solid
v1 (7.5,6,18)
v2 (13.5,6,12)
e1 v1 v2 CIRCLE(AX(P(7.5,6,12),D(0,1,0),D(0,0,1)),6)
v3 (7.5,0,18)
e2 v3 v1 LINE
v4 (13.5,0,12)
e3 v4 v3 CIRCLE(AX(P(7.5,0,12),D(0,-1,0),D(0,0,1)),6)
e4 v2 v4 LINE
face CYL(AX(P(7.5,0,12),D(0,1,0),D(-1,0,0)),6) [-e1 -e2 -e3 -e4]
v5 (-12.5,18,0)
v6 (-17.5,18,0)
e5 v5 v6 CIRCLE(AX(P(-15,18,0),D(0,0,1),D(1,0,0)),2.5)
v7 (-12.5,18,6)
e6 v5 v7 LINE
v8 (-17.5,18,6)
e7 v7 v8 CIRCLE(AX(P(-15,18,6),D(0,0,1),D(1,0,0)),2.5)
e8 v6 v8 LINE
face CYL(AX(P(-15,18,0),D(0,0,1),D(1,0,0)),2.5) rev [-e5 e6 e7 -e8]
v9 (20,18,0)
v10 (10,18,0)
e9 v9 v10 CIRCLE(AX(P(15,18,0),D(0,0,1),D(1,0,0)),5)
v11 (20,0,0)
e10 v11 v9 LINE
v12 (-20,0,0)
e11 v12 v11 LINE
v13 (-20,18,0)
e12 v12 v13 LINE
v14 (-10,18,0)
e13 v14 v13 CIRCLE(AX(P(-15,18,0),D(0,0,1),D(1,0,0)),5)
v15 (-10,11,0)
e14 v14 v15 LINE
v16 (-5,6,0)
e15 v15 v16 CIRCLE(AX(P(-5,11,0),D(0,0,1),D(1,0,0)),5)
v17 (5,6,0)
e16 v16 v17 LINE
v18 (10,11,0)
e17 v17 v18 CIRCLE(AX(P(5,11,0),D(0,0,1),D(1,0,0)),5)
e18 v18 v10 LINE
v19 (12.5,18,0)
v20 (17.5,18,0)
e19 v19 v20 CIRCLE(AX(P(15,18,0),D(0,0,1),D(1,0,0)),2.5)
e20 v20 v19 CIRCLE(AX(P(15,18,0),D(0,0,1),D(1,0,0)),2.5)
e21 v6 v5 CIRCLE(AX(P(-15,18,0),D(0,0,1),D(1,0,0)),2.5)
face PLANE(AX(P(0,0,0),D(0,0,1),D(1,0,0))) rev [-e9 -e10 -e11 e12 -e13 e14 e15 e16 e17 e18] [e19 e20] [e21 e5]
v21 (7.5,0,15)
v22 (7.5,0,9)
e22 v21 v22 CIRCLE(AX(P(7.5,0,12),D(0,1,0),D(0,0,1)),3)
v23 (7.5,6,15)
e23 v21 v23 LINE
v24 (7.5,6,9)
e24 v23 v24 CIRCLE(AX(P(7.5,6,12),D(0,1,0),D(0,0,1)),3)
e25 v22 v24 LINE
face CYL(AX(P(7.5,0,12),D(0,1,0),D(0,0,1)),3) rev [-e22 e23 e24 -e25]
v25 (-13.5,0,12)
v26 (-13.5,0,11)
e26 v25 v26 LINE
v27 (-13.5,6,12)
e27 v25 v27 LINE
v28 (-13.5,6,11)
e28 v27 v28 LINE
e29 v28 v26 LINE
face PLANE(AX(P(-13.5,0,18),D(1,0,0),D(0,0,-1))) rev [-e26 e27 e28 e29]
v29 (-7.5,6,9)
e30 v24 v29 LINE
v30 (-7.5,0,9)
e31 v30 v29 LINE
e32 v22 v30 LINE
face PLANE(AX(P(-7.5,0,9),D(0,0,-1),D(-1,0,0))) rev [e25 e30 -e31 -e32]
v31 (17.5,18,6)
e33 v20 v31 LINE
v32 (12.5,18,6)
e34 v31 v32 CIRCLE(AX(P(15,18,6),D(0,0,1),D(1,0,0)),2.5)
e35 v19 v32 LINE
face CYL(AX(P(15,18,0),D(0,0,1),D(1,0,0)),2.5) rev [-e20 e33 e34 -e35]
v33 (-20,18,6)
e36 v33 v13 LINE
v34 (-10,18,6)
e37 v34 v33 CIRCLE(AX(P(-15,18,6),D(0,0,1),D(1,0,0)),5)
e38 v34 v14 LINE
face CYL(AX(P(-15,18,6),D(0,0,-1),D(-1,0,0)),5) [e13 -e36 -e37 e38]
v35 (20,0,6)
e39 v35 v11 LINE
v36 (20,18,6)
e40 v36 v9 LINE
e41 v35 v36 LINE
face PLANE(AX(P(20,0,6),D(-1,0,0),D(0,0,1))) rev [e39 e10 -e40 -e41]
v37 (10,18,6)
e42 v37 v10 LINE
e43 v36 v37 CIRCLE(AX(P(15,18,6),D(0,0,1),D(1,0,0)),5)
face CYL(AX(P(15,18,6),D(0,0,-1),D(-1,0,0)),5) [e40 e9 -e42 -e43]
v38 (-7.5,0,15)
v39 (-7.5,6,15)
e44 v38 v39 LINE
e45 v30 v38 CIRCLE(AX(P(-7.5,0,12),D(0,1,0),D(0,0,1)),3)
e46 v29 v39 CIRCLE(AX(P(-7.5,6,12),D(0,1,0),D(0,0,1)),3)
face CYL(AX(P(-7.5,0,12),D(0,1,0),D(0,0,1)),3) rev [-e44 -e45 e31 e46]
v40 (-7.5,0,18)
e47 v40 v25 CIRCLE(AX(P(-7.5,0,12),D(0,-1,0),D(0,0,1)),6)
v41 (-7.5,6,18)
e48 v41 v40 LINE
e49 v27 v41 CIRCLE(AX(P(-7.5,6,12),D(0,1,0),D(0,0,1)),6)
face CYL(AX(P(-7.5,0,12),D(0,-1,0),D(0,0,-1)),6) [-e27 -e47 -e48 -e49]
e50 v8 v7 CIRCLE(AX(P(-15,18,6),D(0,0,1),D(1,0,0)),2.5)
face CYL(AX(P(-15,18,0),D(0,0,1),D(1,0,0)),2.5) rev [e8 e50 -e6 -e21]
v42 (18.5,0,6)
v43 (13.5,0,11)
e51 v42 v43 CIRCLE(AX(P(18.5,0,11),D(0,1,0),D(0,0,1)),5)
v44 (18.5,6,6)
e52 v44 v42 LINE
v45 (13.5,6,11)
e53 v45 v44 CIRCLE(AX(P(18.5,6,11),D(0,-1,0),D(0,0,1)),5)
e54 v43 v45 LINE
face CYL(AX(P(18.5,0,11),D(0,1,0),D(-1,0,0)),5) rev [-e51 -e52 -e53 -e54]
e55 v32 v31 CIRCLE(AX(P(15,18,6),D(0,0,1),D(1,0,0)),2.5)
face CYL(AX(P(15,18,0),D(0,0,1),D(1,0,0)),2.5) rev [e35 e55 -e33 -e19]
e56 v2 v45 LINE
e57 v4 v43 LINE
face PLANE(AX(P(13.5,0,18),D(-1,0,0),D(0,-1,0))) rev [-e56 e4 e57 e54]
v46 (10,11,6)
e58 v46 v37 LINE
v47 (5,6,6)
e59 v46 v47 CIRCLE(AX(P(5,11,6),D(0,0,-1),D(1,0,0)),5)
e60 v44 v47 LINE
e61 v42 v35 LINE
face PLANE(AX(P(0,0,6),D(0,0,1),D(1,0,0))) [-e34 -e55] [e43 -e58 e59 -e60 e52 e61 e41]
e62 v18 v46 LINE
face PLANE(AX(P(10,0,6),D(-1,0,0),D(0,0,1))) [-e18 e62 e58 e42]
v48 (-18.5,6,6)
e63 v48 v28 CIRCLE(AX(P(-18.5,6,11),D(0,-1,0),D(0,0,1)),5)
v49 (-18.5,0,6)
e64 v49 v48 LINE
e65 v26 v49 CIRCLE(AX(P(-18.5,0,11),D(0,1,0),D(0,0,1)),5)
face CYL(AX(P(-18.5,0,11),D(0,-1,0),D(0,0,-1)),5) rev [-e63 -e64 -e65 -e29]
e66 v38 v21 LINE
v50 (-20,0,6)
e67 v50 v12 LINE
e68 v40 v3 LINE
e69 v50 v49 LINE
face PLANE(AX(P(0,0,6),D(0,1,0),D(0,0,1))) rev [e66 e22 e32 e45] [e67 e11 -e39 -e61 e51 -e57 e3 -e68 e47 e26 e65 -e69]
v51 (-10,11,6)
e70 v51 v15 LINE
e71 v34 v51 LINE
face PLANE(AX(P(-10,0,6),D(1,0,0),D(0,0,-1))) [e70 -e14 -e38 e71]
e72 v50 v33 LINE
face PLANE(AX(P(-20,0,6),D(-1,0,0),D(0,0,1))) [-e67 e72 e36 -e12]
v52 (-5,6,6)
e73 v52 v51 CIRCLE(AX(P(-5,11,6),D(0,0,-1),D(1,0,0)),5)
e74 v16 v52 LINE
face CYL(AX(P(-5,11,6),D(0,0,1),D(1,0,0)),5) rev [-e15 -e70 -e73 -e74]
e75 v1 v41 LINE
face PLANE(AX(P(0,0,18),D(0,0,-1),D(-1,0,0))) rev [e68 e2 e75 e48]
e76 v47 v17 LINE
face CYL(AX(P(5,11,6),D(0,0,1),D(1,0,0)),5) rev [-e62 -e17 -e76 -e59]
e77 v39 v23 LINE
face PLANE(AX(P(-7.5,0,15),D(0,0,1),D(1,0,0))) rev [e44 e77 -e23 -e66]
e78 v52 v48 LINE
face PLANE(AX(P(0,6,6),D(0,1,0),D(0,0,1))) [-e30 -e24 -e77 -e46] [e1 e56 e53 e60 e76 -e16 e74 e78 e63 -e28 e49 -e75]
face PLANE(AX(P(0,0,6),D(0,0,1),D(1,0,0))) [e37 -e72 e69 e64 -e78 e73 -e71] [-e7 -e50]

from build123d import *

# Parameters (mm, degrees)
BRACKET_PROFILE_DEPTH     = 6
UPRIGHT_ROUNDS_R5_R       = 5
BASE_PLATE_SKETCH_W       = 27
BASE_PLATE_SKETCH_H       = 6
BASE_PLATE_DEPTH          = 12
BASE_PLATE_ROUNDS_R6_R    = 6
BASE_UPRIGHT_FILLETS_R5_R = 5
BASE_SLOT_DEPTH           = 6
PIVOT_HOLES_SKETCH_R      = 2.5
PIVOT_HOLES_2X_5_DEPTH    = 6


with BuildPart() as part:
    # Bracket Profile Sketch → Bracket Profile (new body)
    with BuildSketch(Plane.XY):
        with BuildLine():
            Line((-20, 0), (20, 0))
            Line((20, 0), (20, 18))
            ThreePointArc((20, 18), (15, 23), (10, 18))
            Line((10, 18), (10, 6))
            Line((10, 6), (-10, 6))
            Line((-10, 6), (-10, 18))
            ThreePointArc((-10, 18), (-15, 23), (-20, 18))
            Line((-20, 18), (-20, 0))
        make_face()
    extrude(amount=BRACKET_PROFILE_DEPTH)

    # Upright Rounds R5
    upright_rounds_r5_edges = [part.edges().sort_by_distance(p)[0] for p in [
        (-10, 6, 3),
        (10, 6, 3),
    ]]
    fillet(upright_rounds_r5_edges, radius=UPRIGHT_ROUNDS_R5_R)

    # Base Plate Sketch → Base Plate (add)
    with BuildSketch(Plane.XY.offset(6)):
        with Locations((0, 3)):
            Rectangle(BASE_PLATE_SKETCH_W, BASE_PLATE_SKETCH_H)
    extrude(amount=BASE_PLATE_DEPTH)

    # Base Plate Rounds R6
    base_plate_rounds_r6_edges = [part.edges().sort_by_distance(p)[0] for p in [
        (-13.5, 3, 18),
        (13.5, 3, 18),
    ]]
    fillet(base_plate_rounds_r6_edges, radius=BASE_PLATE_ROUNDS_R6_R)

    # Base-Upright Fillets R5
    base_upright_fillets_r5_edges = [part.edges().sort_by_distance(p)[0] for p in [
        (-13.5, 3, 6),
        (13.5, 3, 6),
    ]]
    fillet(base_upright_fillets_r5_edges, radius=BASE_UPRIGHT_FILLETS_R5_R)

    # Base Slot Sketch → Base Slot (cut)
    with BuildSketch(Plane(origin=(0, 6, 0), x_dir=(1, 0, 0), z_dir=(0, 1, 0))):
        with BuildLine():
            Line((-7.5, -9), (7.5, -9))
            ThreePointArc((7.5, -9), (10.5, -12), (7.5, -15))
            Line((7.5, -15), (-7.5, -15))
            ThreePointArc((-7.5, -15), (-10.5, -12), (-7.5, -9))
        make_face()
    extrude(amount=-BASE_SLOT_DEPTH, mode=Mode.SUBTRACT)

    # Pivot Holes Sketch → Pivot Holes 2xØ5 (cut)
    with BuildSketch(Plane.XY.offset(6)):
        with Locations((-15, 18)):
            Circle(PIVOT_HOLES_SKETCH_R)
        with Locations((15, 18)):
            Circle(PIVOT_HOLES_SKETCH_R)
    extrude(amount=-PIVOT_HOLES_2X_5_DEPTH, mode=Mode.SUBTRACT)


solid = part.part
